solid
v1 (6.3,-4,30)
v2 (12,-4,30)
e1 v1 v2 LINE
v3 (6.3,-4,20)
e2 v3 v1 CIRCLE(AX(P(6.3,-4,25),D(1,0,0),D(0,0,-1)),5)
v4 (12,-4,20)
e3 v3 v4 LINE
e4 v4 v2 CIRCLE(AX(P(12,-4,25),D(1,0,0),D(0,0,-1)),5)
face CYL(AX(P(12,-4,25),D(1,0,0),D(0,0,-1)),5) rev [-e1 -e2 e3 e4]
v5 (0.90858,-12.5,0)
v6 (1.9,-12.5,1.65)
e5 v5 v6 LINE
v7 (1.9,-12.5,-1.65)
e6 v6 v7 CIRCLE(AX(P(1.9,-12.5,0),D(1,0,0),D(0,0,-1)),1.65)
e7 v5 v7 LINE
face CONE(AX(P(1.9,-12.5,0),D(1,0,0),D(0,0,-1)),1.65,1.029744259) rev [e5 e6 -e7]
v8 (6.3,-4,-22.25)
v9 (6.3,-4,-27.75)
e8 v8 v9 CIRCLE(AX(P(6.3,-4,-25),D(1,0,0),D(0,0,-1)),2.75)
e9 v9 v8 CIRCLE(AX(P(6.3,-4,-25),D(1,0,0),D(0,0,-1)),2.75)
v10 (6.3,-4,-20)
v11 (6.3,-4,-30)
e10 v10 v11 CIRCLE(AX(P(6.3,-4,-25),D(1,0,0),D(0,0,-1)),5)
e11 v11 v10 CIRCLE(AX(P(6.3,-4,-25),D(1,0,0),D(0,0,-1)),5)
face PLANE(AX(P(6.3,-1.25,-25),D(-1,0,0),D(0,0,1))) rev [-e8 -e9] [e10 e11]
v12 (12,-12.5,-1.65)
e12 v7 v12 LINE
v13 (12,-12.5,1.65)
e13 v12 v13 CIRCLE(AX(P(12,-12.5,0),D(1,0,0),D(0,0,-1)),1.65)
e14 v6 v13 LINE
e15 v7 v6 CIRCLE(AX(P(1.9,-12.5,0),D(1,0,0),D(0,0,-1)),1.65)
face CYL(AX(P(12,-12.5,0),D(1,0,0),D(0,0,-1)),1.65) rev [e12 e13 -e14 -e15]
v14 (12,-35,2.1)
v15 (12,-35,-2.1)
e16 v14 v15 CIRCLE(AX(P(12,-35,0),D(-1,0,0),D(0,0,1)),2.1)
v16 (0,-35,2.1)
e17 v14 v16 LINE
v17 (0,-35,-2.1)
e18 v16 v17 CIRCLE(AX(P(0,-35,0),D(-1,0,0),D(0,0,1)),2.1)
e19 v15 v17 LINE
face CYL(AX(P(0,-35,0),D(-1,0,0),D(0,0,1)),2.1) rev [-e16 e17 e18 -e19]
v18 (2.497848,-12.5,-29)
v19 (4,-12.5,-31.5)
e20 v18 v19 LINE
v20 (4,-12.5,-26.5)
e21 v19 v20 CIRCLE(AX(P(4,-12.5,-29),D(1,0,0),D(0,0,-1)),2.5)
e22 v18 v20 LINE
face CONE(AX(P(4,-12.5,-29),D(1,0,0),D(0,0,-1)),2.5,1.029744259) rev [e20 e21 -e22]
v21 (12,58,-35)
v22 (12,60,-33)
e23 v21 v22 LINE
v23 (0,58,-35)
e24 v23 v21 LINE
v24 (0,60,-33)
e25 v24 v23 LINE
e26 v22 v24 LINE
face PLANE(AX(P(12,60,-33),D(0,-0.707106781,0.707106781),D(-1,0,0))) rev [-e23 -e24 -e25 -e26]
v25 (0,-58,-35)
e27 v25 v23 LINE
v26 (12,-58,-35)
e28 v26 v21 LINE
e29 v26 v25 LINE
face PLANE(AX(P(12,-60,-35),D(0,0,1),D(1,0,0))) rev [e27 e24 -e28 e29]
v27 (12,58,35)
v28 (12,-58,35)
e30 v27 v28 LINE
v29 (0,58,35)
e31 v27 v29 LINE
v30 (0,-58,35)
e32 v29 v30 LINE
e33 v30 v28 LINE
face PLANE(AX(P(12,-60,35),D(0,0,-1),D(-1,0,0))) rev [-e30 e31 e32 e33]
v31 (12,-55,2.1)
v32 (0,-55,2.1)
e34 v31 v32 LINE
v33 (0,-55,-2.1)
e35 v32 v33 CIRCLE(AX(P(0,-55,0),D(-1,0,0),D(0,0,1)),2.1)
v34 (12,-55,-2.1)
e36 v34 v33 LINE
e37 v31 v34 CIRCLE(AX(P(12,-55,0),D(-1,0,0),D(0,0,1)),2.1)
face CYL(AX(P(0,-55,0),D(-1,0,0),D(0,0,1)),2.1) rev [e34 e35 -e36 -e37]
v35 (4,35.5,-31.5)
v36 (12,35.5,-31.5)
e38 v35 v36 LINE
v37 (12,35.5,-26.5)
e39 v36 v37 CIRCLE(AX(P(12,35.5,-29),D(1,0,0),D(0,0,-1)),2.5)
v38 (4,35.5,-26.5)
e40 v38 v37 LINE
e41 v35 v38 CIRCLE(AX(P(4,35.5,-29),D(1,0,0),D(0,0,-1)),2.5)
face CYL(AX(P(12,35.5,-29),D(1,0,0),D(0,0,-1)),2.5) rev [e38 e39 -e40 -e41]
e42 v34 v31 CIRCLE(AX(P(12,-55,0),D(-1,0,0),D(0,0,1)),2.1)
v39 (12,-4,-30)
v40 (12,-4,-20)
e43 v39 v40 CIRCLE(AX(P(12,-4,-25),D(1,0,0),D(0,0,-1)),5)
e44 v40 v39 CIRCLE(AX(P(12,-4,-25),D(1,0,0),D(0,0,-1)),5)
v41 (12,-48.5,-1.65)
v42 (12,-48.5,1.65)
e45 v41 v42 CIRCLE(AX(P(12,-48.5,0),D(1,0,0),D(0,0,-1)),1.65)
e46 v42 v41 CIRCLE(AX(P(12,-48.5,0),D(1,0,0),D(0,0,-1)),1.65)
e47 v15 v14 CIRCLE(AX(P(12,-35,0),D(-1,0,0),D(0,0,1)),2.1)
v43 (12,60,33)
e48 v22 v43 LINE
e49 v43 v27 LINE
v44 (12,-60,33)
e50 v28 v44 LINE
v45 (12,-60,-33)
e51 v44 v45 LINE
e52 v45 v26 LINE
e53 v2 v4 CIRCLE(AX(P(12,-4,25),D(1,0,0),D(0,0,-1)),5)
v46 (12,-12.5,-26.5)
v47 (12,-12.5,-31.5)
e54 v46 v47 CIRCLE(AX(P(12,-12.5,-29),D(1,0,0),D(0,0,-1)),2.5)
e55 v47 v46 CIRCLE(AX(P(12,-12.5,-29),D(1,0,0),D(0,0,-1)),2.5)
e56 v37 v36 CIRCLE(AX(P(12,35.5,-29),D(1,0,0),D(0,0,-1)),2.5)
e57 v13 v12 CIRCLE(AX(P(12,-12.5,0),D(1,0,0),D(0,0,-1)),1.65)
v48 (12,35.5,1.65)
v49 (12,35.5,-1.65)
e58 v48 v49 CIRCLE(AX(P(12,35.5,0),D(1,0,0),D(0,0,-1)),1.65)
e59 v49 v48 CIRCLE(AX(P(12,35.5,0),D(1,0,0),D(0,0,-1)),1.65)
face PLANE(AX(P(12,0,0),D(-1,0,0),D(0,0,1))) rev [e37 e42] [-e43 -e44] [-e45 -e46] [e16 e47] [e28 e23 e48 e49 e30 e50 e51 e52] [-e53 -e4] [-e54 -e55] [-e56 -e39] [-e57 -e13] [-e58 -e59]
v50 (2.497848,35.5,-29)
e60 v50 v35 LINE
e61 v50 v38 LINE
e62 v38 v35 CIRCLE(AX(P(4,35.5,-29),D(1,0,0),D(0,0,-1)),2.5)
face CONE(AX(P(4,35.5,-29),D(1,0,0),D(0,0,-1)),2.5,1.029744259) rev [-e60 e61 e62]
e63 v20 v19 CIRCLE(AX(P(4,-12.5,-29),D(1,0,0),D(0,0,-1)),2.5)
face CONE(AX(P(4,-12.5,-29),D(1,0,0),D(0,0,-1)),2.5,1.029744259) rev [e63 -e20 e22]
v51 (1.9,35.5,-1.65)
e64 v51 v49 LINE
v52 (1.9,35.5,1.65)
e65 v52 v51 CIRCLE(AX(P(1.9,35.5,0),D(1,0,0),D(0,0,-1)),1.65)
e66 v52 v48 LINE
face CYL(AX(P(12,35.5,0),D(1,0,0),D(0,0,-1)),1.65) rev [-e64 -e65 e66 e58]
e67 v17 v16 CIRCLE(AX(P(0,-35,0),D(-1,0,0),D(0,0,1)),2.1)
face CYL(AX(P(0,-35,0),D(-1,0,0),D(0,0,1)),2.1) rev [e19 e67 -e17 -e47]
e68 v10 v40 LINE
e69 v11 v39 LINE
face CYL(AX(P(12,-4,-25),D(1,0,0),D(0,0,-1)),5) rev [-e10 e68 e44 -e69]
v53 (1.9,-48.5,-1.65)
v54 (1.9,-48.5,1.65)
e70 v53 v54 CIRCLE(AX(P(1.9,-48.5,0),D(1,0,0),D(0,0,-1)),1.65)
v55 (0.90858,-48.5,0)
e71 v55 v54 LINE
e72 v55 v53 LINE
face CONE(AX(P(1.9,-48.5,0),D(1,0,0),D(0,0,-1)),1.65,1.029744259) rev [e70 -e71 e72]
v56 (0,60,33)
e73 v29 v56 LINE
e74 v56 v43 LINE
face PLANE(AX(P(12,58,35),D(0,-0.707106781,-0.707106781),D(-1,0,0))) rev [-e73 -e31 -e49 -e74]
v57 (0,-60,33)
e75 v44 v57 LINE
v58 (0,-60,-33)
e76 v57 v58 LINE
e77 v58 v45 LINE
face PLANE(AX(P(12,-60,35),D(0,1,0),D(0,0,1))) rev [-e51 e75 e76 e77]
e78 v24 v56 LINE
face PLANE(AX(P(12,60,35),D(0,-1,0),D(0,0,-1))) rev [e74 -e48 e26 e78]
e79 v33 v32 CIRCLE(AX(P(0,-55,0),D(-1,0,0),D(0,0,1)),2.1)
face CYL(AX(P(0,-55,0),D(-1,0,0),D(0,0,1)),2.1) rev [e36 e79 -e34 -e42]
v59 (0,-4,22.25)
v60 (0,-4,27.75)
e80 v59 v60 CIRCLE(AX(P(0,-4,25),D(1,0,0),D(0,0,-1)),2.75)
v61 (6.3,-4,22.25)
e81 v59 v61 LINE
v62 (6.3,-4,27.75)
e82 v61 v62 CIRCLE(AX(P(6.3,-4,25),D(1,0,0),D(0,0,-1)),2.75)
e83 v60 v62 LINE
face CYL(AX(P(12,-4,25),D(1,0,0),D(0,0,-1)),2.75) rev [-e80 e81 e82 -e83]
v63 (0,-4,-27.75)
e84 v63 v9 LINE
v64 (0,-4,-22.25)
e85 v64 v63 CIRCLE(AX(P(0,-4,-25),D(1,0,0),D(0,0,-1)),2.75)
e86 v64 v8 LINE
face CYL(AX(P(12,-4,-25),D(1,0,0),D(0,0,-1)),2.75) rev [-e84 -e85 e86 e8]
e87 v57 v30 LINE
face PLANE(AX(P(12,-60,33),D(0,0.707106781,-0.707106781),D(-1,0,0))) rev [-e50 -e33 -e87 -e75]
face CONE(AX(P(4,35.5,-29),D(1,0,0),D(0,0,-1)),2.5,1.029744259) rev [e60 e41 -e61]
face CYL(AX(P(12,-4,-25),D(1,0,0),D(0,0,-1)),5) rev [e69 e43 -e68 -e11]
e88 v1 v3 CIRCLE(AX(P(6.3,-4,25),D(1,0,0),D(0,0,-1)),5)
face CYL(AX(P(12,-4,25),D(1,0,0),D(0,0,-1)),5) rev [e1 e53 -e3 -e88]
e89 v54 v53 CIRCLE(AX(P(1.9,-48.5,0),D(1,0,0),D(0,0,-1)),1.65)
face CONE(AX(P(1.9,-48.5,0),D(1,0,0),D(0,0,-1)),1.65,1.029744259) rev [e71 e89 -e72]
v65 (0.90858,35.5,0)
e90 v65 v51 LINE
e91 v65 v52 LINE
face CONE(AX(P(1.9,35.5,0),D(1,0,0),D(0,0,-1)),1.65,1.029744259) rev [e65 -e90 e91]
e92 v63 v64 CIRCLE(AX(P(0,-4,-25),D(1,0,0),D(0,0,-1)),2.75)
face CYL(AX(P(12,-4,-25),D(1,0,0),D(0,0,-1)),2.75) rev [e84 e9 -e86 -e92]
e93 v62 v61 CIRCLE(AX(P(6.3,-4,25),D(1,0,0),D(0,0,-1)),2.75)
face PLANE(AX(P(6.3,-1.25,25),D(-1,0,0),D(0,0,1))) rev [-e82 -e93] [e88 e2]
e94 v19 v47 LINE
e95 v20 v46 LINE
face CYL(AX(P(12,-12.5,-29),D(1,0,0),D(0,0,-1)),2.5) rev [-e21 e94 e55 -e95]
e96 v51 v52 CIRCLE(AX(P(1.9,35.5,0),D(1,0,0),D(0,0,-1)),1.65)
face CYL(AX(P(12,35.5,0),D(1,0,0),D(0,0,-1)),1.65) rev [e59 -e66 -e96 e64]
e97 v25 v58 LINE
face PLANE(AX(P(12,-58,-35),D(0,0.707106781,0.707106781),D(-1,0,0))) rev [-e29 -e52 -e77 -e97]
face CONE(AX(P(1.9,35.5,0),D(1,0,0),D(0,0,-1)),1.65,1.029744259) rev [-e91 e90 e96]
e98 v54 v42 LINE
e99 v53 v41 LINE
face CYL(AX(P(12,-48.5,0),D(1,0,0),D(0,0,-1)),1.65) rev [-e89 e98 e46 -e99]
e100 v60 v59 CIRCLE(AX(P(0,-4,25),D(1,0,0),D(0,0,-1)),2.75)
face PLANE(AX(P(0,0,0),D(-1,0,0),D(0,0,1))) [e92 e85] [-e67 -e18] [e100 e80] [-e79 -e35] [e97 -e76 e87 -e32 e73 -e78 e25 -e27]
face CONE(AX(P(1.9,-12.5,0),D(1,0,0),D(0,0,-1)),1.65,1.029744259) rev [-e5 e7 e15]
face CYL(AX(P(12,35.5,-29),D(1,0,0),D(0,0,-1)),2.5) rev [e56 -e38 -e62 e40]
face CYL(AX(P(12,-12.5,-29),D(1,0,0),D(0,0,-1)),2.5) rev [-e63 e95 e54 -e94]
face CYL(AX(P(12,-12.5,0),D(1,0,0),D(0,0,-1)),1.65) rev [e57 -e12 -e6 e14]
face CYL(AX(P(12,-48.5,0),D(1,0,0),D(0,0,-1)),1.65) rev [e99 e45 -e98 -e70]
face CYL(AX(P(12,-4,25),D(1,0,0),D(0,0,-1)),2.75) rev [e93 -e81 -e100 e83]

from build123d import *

# Parameters (mm, degrees)
SKETCH1_W                                            = 70
SKETCH1_H                                            = 120
BOSS_EXTRUDE1_DEPTH                                  = 12
M5_TAPPED_HOLE1_D                                    = 4.2
M5_TAPPED_HOLE1_DEPTH                                = 12.4
M5_TAPPED_HOLE1_TIP                                  = 1.2618073
CBORE_FOR_M5_HEXAGON_SOCKET_HEAD_CAP_SCR_D           = 5.5
CBORE_FOR_M5_HEXAGON_SOCKET_HEAD_CAP_SCR_CBORE_D     = 10
CBORE_FOR_M5_HEXAGON_SOCKET_HEAD_CAP_SCR_CBORE_DEPTH = 5.7
M4_TAPPED_HOLE1_D                                    = 3.3
M4_TAPPED_HOLE1_DEPTH                                = 10.1
M4_TAPPED_HOLE1_TIP                                  = 0.991420021
F_5_0MM_DOWEL_HOLE1_D                                = 5
F_5_0MM_DOWEL_HOLE1_DEPTH                            = 8
F_5_0MM_DOWEL_HOLE1_TIP                              = 1.502151548
CHAMFER1_SIZE                                        = 2


with BuildPart() as part:
    # Sketch1 → Boss-Extrude1 (new body)
    with BuildSketch(Plane(origin=(0, 0, 0), x_dir=(0, 0, -1), z_dir=(1, 0, 0))):
        Rectangle(SKETCH1_W, SKETCH1_H)
    extrude(amount=BOSS_EXTRUDE1_DEPTH)

    # M5 Tapped Hole1
    with Locations(Plane.ZY):
        with Locations((0, -35), (0, -55)):
            Hole(M5_TAPPED_HOLE1_D / 2, depth=M5_TAPPED_HOLE1_DEPTH)
            with Locations((0, 0, -(M5_TAPPED_HOLE1_DEPTH + M5_TAPPED_HOLE1_TIP / 2))):  # 118° drill point
                Cone(0, M5_TAPPED_HOLE1_D / 2, M5_TAPPED_HOLE1_TIP, mode=Mode.SUBTRACT)

    # CBORE for M5 Hexagon socket head cap screws1 (through all)
    with Locations(Plane(origin=(12, 0, 0), x_dir=(0, 0, -1), z_dir=(1, 0, 0))):
        with Locations((25, -4), (-25, -4)):
            CounterBoreHole(CBORE_FOR_M5_HEXAGON_SOCKET_HEAD_CAP_SCR_D / 2, CBORE_FOR_M5_HEXAGON_SOCKET_HEAD_CAP_SCR_CBORE_D / 2, CBORE_FOR_M5_HEXAGON_SOCKET_HEAD_CAP_SCR_CBORE_DEPTH)

    # M4 Tapped Hole1
    with Locations(Plane(origin=(12, 0, 0), x_dir=(0, 0, -1), z_dir=(1, 0, 0))):
        with Locations((0, -48.5), (0, -12.5), (0, 35.5)):
            Hole(M4_TAPPED_HOLE1_D / 2, depth=M4_TAPPED_HOLE1_DEPTH)
            with Locations((0, 0, -(M4_TAPPED_HOLE1_DEPTH + M4_TAPPED_HOLE1_TIP / 2))):  # 118° drill point
                Cone(0, M4_TAPPED_HOLE1_D / 2, M4_TAPPED_HOLE1_TIP, mode=Mode.SUBTRACT)

    # Ø5.0mm Dowel Hole1
    with Locations(Plane(origin=(12, 0, 0), x_dir=(0, 0, -1), z_dir=(1, 0, 0))):
        with Locations((29, 35.5), (29, -12.5)):
            Hole(F_5_0MM_DOWEL_HOLE1_D / 2, depth=F_5_0MM_DOWEL_HOLE1_DEPTH)
            with Locations((0, 0, -(F_5_0MM_DOWEL_HOLE1_DEPTH + F_5_0MM_DOWEL_HOLE1_TIP / 2))):  # 118° drill point
                Cone(0, F_5_0MM_DOWEL_HOLE1_D / 2, F_5_0MM_DOWEL_HOLE1_TIP, mode=Mode.SUBTRACT)

    # Chamfer1
    chamfer1_edges = [part.edges().sort_by_distance(p)[0] for p in [
        (6, -60, -35),
        (6, -60, 35),
        (6, 60, 35),
        (6, 60, -35),
    ]]
    chamfer(chamfer1_edges, length=CHAMFER1_SIZE)


solid = part.part
